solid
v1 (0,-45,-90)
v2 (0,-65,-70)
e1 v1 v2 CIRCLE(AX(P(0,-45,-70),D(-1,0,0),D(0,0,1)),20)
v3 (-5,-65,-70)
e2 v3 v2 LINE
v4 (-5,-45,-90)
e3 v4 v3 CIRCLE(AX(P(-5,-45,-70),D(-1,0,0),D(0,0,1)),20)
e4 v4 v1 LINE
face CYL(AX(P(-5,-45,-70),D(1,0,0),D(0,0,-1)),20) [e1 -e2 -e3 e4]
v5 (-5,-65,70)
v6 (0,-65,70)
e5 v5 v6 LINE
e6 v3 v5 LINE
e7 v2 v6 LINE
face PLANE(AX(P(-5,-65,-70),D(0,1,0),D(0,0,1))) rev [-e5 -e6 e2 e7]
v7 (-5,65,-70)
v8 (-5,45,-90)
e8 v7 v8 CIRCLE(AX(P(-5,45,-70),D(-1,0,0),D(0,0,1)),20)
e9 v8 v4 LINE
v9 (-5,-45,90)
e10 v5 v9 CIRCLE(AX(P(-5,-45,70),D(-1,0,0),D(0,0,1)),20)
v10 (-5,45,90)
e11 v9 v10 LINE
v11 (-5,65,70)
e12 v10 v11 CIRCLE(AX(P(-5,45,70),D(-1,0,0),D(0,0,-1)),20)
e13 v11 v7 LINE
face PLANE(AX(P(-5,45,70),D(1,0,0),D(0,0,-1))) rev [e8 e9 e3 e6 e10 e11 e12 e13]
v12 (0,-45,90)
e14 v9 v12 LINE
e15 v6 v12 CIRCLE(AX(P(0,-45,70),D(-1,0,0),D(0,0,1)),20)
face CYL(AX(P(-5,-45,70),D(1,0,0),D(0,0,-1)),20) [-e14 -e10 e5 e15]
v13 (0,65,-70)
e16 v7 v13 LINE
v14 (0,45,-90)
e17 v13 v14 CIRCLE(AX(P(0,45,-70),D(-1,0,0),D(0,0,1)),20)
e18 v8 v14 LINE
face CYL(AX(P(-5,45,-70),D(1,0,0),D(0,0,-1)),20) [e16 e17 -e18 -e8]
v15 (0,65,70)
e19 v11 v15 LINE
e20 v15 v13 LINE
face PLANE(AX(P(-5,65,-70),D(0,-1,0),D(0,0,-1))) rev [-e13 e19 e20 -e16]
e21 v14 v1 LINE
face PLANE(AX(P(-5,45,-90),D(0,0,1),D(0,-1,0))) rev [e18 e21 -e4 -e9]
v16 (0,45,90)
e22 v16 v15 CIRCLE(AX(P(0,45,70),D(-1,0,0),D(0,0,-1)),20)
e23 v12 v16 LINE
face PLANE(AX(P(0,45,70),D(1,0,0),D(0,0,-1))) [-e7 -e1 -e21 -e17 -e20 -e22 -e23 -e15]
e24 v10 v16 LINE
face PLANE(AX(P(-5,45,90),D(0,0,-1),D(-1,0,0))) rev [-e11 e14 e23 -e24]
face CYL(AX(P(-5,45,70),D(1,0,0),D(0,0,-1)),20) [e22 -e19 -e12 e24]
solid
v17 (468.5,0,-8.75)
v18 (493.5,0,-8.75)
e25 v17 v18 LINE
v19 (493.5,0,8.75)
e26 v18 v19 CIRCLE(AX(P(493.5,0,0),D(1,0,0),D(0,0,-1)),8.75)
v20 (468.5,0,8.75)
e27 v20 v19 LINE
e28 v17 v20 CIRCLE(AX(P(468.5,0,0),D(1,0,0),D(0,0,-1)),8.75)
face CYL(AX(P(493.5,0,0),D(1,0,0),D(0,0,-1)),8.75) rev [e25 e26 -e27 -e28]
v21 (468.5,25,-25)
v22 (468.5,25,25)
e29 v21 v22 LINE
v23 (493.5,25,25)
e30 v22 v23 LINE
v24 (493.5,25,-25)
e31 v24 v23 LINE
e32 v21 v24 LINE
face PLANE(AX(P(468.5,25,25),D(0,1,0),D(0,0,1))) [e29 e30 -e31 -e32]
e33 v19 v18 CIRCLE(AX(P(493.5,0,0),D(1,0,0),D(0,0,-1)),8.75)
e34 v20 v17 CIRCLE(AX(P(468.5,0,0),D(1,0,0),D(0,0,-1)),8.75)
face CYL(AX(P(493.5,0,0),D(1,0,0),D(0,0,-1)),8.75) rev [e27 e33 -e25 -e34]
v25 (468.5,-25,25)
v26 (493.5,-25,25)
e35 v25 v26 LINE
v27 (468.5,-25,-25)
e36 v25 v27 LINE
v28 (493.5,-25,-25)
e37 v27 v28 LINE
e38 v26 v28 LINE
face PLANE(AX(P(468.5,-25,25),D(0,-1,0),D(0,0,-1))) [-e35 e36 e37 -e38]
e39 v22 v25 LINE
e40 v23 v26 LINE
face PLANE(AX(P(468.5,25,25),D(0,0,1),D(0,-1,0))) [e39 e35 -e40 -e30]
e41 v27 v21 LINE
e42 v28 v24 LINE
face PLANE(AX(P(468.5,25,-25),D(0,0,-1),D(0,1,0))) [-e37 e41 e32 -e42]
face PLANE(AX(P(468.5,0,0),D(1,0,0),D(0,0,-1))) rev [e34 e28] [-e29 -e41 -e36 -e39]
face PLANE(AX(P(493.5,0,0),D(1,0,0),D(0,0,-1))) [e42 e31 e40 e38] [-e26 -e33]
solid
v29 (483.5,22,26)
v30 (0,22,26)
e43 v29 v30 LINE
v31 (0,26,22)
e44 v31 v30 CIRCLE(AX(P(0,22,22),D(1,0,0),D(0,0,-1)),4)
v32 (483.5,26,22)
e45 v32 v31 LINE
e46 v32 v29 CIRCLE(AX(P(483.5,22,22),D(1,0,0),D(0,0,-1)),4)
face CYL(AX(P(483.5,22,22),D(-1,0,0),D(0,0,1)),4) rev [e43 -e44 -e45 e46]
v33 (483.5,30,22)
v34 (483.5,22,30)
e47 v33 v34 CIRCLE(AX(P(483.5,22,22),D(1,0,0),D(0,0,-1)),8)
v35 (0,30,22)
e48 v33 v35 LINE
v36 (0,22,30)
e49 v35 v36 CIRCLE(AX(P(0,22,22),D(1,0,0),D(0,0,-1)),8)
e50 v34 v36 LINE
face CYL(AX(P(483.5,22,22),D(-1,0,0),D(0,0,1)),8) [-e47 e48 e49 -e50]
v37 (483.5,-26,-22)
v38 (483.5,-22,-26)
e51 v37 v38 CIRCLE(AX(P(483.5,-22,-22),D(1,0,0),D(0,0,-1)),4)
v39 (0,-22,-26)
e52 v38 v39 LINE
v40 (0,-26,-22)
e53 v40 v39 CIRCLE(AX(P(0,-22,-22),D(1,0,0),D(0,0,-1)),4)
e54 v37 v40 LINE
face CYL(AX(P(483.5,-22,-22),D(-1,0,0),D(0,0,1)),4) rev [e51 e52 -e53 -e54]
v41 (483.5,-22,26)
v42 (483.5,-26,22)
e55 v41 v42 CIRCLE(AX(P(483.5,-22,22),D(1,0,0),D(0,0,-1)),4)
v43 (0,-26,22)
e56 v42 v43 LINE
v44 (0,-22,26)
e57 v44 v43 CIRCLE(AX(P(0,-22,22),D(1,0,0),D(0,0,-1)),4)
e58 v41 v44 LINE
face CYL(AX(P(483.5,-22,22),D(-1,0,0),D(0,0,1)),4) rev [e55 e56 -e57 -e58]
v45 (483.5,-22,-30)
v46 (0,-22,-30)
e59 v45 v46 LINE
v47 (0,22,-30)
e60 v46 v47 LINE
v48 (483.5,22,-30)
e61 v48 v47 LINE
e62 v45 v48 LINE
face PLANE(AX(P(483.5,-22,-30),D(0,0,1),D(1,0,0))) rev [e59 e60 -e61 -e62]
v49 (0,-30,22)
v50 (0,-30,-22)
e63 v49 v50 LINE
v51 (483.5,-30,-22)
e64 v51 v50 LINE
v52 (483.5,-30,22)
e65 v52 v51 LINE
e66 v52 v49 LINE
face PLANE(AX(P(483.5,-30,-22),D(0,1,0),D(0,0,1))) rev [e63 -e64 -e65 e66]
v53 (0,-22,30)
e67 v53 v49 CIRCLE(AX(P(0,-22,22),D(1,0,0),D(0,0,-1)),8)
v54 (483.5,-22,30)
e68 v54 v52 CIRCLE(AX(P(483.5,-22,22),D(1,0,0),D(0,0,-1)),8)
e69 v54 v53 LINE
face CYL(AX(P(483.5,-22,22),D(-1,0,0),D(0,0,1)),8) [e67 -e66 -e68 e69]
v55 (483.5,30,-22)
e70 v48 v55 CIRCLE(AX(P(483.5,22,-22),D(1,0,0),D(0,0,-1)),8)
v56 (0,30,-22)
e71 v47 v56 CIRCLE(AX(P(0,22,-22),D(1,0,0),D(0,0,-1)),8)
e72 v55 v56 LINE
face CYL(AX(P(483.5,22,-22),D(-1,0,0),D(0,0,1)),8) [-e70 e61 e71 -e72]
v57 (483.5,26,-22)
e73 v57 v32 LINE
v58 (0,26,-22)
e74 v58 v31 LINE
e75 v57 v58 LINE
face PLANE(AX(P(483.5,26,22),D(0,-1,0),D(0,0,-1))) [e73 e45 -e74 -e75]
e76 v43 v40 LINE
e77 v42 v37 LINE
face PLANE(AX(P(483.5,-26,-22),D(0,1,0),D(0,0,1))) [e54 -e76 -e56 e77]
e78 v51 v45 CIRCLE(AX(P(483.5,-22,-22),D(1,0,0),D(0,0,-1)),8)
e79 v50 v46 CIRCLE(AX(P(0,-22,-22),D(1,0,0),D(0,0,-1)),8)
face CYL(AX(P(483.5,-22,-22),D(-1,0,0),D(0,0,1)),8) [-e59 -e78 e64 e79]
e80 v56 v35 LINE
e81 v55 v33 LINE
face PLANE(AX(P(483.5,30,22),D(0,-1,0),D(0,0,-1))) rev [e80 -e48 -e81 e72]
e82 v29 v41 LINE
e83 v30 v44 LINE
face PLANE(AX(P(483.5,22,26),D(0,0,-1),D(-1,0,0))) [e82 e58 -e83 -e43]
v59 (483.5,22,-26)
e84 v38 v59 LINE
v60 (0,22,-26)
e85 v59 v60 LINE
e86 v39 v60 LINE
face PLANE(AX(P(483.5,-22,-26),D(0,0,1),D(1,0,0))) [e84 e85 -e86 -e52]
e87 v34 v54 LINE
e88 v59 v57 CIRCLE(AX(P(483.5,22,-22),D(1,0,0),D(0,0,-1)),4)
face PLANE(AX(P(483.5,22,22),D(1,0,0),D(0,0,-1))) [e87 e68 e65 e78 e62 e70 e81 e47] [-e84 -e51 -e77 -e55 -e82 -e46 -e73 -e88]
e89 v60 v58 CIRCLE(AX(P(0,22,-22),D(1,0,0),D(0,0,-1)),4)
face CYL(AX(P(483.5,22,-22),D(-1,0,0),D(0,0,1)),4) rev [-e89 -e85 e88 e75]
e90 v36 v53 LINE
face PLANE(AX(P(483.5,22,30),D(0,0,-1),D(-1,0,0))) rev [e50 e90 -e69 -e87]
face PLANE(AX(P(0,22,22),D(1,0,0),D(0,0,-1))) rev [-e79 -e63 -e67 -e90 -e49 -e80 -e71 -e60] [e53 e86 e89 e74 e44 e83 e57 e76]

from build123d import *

# Parameters (mm, degrees)
GB_T6728_2002_60_X_60_X_4_1_DEPTH = 483.5
EXTRUDE_1_DEPTH                   = 5
EXTRUDE_2_DEPTH                   = 10
EXTRUDE_2_DEPTH_BACK              = 15
SKETCH_6_W                        = 50
SKETCH_6_H                        = 50


with BuildPart() as part:
    # Sketch1 → 冷弯空心方管gb∕t6728-2002 60 X 60 X 4(1) (new body)
    with BuildSketch(Plane.YZ):
        with BuildLine():
            Line((-22, -30), (22, -30))
            ThreePointArc((22, -30), (27.656854249, -27.656854249), (30, -22))
            Line((30, -22), (30, 22))
            ThreePointArc((30, 22), (27.656854249, 27.656854249), (22, 30))
            Line((22, 30), (-22, 30))
            ThreePointArc((-22, 30), (-27.656854249, 27.656854249), (-30, 22))
            Line((-30, 22), (-30, -22))
            ThreePointArc((-30, -22), (-27.656854249, -27.656854249), (-22, -30))
        make_face()
        with BuildLine():
            Line((-22, -26), (22, -26))
            ThreePointArc((22, -26), (24.828427125, -24.828427125), (26, -22))
            Line((26, -22), (26, 22))
            ThreePointArc((26, 22), (24.828427125, 24.828427125), (22, 26))
            Line((22, 26), (-22, 26))
            ThreePointArc((-22, 26), (-24.828427125, 24.828427125), (-26, 22))
            Line((-26, 22), (-26, -22))
            ThreePointArc((-26, -22), (-24.828427125, -24.828427125), (-22, -26))
        make_face(mode=Mode.SUBTRACT)
    extrude(amount=GB_T6728_2002_60_X_60_X_4_1_DEPTH)


with BuildPart() as body_2:
    # 草图3 → 凸台-拉伸1 (new body)
    with BuildSketch(Plane.ZY):
        with BuildLine():
            Line((-70, 65), (70, 65))
            ThreePointArc((70, 65), (84.142135624, 59.142135624), (90, 45))
            Line((90, 45), (90, -45))
            ThreePointArc((90, -45), (84.142135624, -59.142135624), (70, -65))
            Line((70, -65), (-70, -65))
            ThreePointArc((-70, -65), (-84.142135624, -59.142135624), (-90, -45))
            Line((-90, -45), (-90, 45))
            ThreePointArc((-90, 45), (-84.142135624, 59.142135624), (-70, 65))
        make_face()
    extrude(amount=EXTRUDE_1_DEPTH)


with BuildPart() as body_3:
    # 草图6 → 凸台-拉伸2 (new, two sides: drawn at the far end of the back side and taken through both)
    with BuildSketch(Plane(origin=(483.5, 0, 0), x_dir=(0, 0, -1), z_dir=(1, 0, 0)).offset(-EXTRUDE_2_DEPTH_BACK)):
        Rectangle(SKETCH_6_W, SKETCH_6_H)
    extrude(amount=EXTRUDE_2_DEPTH + EXTRUDE_2_DEPTH_BACK)

    # 草图8 → M20 螺纹孔1 (revolve, cut)
    with BuildSketch(Plane(origin=(493.5, 0, 0), x_dir=(0, 0, -1), z_dir=(0, 1, 0))):
        Polygon((0, 0), (0, 57.757530416), (8.75, 52.5), (8.75, 0), align=None)
    revolve(axis=Axis((499.85, 0, 0), (-1, 0, 0)), mode=Mode.SUBTRACT)


solid = Compound([part.part, body_2.part, body_3.part])
